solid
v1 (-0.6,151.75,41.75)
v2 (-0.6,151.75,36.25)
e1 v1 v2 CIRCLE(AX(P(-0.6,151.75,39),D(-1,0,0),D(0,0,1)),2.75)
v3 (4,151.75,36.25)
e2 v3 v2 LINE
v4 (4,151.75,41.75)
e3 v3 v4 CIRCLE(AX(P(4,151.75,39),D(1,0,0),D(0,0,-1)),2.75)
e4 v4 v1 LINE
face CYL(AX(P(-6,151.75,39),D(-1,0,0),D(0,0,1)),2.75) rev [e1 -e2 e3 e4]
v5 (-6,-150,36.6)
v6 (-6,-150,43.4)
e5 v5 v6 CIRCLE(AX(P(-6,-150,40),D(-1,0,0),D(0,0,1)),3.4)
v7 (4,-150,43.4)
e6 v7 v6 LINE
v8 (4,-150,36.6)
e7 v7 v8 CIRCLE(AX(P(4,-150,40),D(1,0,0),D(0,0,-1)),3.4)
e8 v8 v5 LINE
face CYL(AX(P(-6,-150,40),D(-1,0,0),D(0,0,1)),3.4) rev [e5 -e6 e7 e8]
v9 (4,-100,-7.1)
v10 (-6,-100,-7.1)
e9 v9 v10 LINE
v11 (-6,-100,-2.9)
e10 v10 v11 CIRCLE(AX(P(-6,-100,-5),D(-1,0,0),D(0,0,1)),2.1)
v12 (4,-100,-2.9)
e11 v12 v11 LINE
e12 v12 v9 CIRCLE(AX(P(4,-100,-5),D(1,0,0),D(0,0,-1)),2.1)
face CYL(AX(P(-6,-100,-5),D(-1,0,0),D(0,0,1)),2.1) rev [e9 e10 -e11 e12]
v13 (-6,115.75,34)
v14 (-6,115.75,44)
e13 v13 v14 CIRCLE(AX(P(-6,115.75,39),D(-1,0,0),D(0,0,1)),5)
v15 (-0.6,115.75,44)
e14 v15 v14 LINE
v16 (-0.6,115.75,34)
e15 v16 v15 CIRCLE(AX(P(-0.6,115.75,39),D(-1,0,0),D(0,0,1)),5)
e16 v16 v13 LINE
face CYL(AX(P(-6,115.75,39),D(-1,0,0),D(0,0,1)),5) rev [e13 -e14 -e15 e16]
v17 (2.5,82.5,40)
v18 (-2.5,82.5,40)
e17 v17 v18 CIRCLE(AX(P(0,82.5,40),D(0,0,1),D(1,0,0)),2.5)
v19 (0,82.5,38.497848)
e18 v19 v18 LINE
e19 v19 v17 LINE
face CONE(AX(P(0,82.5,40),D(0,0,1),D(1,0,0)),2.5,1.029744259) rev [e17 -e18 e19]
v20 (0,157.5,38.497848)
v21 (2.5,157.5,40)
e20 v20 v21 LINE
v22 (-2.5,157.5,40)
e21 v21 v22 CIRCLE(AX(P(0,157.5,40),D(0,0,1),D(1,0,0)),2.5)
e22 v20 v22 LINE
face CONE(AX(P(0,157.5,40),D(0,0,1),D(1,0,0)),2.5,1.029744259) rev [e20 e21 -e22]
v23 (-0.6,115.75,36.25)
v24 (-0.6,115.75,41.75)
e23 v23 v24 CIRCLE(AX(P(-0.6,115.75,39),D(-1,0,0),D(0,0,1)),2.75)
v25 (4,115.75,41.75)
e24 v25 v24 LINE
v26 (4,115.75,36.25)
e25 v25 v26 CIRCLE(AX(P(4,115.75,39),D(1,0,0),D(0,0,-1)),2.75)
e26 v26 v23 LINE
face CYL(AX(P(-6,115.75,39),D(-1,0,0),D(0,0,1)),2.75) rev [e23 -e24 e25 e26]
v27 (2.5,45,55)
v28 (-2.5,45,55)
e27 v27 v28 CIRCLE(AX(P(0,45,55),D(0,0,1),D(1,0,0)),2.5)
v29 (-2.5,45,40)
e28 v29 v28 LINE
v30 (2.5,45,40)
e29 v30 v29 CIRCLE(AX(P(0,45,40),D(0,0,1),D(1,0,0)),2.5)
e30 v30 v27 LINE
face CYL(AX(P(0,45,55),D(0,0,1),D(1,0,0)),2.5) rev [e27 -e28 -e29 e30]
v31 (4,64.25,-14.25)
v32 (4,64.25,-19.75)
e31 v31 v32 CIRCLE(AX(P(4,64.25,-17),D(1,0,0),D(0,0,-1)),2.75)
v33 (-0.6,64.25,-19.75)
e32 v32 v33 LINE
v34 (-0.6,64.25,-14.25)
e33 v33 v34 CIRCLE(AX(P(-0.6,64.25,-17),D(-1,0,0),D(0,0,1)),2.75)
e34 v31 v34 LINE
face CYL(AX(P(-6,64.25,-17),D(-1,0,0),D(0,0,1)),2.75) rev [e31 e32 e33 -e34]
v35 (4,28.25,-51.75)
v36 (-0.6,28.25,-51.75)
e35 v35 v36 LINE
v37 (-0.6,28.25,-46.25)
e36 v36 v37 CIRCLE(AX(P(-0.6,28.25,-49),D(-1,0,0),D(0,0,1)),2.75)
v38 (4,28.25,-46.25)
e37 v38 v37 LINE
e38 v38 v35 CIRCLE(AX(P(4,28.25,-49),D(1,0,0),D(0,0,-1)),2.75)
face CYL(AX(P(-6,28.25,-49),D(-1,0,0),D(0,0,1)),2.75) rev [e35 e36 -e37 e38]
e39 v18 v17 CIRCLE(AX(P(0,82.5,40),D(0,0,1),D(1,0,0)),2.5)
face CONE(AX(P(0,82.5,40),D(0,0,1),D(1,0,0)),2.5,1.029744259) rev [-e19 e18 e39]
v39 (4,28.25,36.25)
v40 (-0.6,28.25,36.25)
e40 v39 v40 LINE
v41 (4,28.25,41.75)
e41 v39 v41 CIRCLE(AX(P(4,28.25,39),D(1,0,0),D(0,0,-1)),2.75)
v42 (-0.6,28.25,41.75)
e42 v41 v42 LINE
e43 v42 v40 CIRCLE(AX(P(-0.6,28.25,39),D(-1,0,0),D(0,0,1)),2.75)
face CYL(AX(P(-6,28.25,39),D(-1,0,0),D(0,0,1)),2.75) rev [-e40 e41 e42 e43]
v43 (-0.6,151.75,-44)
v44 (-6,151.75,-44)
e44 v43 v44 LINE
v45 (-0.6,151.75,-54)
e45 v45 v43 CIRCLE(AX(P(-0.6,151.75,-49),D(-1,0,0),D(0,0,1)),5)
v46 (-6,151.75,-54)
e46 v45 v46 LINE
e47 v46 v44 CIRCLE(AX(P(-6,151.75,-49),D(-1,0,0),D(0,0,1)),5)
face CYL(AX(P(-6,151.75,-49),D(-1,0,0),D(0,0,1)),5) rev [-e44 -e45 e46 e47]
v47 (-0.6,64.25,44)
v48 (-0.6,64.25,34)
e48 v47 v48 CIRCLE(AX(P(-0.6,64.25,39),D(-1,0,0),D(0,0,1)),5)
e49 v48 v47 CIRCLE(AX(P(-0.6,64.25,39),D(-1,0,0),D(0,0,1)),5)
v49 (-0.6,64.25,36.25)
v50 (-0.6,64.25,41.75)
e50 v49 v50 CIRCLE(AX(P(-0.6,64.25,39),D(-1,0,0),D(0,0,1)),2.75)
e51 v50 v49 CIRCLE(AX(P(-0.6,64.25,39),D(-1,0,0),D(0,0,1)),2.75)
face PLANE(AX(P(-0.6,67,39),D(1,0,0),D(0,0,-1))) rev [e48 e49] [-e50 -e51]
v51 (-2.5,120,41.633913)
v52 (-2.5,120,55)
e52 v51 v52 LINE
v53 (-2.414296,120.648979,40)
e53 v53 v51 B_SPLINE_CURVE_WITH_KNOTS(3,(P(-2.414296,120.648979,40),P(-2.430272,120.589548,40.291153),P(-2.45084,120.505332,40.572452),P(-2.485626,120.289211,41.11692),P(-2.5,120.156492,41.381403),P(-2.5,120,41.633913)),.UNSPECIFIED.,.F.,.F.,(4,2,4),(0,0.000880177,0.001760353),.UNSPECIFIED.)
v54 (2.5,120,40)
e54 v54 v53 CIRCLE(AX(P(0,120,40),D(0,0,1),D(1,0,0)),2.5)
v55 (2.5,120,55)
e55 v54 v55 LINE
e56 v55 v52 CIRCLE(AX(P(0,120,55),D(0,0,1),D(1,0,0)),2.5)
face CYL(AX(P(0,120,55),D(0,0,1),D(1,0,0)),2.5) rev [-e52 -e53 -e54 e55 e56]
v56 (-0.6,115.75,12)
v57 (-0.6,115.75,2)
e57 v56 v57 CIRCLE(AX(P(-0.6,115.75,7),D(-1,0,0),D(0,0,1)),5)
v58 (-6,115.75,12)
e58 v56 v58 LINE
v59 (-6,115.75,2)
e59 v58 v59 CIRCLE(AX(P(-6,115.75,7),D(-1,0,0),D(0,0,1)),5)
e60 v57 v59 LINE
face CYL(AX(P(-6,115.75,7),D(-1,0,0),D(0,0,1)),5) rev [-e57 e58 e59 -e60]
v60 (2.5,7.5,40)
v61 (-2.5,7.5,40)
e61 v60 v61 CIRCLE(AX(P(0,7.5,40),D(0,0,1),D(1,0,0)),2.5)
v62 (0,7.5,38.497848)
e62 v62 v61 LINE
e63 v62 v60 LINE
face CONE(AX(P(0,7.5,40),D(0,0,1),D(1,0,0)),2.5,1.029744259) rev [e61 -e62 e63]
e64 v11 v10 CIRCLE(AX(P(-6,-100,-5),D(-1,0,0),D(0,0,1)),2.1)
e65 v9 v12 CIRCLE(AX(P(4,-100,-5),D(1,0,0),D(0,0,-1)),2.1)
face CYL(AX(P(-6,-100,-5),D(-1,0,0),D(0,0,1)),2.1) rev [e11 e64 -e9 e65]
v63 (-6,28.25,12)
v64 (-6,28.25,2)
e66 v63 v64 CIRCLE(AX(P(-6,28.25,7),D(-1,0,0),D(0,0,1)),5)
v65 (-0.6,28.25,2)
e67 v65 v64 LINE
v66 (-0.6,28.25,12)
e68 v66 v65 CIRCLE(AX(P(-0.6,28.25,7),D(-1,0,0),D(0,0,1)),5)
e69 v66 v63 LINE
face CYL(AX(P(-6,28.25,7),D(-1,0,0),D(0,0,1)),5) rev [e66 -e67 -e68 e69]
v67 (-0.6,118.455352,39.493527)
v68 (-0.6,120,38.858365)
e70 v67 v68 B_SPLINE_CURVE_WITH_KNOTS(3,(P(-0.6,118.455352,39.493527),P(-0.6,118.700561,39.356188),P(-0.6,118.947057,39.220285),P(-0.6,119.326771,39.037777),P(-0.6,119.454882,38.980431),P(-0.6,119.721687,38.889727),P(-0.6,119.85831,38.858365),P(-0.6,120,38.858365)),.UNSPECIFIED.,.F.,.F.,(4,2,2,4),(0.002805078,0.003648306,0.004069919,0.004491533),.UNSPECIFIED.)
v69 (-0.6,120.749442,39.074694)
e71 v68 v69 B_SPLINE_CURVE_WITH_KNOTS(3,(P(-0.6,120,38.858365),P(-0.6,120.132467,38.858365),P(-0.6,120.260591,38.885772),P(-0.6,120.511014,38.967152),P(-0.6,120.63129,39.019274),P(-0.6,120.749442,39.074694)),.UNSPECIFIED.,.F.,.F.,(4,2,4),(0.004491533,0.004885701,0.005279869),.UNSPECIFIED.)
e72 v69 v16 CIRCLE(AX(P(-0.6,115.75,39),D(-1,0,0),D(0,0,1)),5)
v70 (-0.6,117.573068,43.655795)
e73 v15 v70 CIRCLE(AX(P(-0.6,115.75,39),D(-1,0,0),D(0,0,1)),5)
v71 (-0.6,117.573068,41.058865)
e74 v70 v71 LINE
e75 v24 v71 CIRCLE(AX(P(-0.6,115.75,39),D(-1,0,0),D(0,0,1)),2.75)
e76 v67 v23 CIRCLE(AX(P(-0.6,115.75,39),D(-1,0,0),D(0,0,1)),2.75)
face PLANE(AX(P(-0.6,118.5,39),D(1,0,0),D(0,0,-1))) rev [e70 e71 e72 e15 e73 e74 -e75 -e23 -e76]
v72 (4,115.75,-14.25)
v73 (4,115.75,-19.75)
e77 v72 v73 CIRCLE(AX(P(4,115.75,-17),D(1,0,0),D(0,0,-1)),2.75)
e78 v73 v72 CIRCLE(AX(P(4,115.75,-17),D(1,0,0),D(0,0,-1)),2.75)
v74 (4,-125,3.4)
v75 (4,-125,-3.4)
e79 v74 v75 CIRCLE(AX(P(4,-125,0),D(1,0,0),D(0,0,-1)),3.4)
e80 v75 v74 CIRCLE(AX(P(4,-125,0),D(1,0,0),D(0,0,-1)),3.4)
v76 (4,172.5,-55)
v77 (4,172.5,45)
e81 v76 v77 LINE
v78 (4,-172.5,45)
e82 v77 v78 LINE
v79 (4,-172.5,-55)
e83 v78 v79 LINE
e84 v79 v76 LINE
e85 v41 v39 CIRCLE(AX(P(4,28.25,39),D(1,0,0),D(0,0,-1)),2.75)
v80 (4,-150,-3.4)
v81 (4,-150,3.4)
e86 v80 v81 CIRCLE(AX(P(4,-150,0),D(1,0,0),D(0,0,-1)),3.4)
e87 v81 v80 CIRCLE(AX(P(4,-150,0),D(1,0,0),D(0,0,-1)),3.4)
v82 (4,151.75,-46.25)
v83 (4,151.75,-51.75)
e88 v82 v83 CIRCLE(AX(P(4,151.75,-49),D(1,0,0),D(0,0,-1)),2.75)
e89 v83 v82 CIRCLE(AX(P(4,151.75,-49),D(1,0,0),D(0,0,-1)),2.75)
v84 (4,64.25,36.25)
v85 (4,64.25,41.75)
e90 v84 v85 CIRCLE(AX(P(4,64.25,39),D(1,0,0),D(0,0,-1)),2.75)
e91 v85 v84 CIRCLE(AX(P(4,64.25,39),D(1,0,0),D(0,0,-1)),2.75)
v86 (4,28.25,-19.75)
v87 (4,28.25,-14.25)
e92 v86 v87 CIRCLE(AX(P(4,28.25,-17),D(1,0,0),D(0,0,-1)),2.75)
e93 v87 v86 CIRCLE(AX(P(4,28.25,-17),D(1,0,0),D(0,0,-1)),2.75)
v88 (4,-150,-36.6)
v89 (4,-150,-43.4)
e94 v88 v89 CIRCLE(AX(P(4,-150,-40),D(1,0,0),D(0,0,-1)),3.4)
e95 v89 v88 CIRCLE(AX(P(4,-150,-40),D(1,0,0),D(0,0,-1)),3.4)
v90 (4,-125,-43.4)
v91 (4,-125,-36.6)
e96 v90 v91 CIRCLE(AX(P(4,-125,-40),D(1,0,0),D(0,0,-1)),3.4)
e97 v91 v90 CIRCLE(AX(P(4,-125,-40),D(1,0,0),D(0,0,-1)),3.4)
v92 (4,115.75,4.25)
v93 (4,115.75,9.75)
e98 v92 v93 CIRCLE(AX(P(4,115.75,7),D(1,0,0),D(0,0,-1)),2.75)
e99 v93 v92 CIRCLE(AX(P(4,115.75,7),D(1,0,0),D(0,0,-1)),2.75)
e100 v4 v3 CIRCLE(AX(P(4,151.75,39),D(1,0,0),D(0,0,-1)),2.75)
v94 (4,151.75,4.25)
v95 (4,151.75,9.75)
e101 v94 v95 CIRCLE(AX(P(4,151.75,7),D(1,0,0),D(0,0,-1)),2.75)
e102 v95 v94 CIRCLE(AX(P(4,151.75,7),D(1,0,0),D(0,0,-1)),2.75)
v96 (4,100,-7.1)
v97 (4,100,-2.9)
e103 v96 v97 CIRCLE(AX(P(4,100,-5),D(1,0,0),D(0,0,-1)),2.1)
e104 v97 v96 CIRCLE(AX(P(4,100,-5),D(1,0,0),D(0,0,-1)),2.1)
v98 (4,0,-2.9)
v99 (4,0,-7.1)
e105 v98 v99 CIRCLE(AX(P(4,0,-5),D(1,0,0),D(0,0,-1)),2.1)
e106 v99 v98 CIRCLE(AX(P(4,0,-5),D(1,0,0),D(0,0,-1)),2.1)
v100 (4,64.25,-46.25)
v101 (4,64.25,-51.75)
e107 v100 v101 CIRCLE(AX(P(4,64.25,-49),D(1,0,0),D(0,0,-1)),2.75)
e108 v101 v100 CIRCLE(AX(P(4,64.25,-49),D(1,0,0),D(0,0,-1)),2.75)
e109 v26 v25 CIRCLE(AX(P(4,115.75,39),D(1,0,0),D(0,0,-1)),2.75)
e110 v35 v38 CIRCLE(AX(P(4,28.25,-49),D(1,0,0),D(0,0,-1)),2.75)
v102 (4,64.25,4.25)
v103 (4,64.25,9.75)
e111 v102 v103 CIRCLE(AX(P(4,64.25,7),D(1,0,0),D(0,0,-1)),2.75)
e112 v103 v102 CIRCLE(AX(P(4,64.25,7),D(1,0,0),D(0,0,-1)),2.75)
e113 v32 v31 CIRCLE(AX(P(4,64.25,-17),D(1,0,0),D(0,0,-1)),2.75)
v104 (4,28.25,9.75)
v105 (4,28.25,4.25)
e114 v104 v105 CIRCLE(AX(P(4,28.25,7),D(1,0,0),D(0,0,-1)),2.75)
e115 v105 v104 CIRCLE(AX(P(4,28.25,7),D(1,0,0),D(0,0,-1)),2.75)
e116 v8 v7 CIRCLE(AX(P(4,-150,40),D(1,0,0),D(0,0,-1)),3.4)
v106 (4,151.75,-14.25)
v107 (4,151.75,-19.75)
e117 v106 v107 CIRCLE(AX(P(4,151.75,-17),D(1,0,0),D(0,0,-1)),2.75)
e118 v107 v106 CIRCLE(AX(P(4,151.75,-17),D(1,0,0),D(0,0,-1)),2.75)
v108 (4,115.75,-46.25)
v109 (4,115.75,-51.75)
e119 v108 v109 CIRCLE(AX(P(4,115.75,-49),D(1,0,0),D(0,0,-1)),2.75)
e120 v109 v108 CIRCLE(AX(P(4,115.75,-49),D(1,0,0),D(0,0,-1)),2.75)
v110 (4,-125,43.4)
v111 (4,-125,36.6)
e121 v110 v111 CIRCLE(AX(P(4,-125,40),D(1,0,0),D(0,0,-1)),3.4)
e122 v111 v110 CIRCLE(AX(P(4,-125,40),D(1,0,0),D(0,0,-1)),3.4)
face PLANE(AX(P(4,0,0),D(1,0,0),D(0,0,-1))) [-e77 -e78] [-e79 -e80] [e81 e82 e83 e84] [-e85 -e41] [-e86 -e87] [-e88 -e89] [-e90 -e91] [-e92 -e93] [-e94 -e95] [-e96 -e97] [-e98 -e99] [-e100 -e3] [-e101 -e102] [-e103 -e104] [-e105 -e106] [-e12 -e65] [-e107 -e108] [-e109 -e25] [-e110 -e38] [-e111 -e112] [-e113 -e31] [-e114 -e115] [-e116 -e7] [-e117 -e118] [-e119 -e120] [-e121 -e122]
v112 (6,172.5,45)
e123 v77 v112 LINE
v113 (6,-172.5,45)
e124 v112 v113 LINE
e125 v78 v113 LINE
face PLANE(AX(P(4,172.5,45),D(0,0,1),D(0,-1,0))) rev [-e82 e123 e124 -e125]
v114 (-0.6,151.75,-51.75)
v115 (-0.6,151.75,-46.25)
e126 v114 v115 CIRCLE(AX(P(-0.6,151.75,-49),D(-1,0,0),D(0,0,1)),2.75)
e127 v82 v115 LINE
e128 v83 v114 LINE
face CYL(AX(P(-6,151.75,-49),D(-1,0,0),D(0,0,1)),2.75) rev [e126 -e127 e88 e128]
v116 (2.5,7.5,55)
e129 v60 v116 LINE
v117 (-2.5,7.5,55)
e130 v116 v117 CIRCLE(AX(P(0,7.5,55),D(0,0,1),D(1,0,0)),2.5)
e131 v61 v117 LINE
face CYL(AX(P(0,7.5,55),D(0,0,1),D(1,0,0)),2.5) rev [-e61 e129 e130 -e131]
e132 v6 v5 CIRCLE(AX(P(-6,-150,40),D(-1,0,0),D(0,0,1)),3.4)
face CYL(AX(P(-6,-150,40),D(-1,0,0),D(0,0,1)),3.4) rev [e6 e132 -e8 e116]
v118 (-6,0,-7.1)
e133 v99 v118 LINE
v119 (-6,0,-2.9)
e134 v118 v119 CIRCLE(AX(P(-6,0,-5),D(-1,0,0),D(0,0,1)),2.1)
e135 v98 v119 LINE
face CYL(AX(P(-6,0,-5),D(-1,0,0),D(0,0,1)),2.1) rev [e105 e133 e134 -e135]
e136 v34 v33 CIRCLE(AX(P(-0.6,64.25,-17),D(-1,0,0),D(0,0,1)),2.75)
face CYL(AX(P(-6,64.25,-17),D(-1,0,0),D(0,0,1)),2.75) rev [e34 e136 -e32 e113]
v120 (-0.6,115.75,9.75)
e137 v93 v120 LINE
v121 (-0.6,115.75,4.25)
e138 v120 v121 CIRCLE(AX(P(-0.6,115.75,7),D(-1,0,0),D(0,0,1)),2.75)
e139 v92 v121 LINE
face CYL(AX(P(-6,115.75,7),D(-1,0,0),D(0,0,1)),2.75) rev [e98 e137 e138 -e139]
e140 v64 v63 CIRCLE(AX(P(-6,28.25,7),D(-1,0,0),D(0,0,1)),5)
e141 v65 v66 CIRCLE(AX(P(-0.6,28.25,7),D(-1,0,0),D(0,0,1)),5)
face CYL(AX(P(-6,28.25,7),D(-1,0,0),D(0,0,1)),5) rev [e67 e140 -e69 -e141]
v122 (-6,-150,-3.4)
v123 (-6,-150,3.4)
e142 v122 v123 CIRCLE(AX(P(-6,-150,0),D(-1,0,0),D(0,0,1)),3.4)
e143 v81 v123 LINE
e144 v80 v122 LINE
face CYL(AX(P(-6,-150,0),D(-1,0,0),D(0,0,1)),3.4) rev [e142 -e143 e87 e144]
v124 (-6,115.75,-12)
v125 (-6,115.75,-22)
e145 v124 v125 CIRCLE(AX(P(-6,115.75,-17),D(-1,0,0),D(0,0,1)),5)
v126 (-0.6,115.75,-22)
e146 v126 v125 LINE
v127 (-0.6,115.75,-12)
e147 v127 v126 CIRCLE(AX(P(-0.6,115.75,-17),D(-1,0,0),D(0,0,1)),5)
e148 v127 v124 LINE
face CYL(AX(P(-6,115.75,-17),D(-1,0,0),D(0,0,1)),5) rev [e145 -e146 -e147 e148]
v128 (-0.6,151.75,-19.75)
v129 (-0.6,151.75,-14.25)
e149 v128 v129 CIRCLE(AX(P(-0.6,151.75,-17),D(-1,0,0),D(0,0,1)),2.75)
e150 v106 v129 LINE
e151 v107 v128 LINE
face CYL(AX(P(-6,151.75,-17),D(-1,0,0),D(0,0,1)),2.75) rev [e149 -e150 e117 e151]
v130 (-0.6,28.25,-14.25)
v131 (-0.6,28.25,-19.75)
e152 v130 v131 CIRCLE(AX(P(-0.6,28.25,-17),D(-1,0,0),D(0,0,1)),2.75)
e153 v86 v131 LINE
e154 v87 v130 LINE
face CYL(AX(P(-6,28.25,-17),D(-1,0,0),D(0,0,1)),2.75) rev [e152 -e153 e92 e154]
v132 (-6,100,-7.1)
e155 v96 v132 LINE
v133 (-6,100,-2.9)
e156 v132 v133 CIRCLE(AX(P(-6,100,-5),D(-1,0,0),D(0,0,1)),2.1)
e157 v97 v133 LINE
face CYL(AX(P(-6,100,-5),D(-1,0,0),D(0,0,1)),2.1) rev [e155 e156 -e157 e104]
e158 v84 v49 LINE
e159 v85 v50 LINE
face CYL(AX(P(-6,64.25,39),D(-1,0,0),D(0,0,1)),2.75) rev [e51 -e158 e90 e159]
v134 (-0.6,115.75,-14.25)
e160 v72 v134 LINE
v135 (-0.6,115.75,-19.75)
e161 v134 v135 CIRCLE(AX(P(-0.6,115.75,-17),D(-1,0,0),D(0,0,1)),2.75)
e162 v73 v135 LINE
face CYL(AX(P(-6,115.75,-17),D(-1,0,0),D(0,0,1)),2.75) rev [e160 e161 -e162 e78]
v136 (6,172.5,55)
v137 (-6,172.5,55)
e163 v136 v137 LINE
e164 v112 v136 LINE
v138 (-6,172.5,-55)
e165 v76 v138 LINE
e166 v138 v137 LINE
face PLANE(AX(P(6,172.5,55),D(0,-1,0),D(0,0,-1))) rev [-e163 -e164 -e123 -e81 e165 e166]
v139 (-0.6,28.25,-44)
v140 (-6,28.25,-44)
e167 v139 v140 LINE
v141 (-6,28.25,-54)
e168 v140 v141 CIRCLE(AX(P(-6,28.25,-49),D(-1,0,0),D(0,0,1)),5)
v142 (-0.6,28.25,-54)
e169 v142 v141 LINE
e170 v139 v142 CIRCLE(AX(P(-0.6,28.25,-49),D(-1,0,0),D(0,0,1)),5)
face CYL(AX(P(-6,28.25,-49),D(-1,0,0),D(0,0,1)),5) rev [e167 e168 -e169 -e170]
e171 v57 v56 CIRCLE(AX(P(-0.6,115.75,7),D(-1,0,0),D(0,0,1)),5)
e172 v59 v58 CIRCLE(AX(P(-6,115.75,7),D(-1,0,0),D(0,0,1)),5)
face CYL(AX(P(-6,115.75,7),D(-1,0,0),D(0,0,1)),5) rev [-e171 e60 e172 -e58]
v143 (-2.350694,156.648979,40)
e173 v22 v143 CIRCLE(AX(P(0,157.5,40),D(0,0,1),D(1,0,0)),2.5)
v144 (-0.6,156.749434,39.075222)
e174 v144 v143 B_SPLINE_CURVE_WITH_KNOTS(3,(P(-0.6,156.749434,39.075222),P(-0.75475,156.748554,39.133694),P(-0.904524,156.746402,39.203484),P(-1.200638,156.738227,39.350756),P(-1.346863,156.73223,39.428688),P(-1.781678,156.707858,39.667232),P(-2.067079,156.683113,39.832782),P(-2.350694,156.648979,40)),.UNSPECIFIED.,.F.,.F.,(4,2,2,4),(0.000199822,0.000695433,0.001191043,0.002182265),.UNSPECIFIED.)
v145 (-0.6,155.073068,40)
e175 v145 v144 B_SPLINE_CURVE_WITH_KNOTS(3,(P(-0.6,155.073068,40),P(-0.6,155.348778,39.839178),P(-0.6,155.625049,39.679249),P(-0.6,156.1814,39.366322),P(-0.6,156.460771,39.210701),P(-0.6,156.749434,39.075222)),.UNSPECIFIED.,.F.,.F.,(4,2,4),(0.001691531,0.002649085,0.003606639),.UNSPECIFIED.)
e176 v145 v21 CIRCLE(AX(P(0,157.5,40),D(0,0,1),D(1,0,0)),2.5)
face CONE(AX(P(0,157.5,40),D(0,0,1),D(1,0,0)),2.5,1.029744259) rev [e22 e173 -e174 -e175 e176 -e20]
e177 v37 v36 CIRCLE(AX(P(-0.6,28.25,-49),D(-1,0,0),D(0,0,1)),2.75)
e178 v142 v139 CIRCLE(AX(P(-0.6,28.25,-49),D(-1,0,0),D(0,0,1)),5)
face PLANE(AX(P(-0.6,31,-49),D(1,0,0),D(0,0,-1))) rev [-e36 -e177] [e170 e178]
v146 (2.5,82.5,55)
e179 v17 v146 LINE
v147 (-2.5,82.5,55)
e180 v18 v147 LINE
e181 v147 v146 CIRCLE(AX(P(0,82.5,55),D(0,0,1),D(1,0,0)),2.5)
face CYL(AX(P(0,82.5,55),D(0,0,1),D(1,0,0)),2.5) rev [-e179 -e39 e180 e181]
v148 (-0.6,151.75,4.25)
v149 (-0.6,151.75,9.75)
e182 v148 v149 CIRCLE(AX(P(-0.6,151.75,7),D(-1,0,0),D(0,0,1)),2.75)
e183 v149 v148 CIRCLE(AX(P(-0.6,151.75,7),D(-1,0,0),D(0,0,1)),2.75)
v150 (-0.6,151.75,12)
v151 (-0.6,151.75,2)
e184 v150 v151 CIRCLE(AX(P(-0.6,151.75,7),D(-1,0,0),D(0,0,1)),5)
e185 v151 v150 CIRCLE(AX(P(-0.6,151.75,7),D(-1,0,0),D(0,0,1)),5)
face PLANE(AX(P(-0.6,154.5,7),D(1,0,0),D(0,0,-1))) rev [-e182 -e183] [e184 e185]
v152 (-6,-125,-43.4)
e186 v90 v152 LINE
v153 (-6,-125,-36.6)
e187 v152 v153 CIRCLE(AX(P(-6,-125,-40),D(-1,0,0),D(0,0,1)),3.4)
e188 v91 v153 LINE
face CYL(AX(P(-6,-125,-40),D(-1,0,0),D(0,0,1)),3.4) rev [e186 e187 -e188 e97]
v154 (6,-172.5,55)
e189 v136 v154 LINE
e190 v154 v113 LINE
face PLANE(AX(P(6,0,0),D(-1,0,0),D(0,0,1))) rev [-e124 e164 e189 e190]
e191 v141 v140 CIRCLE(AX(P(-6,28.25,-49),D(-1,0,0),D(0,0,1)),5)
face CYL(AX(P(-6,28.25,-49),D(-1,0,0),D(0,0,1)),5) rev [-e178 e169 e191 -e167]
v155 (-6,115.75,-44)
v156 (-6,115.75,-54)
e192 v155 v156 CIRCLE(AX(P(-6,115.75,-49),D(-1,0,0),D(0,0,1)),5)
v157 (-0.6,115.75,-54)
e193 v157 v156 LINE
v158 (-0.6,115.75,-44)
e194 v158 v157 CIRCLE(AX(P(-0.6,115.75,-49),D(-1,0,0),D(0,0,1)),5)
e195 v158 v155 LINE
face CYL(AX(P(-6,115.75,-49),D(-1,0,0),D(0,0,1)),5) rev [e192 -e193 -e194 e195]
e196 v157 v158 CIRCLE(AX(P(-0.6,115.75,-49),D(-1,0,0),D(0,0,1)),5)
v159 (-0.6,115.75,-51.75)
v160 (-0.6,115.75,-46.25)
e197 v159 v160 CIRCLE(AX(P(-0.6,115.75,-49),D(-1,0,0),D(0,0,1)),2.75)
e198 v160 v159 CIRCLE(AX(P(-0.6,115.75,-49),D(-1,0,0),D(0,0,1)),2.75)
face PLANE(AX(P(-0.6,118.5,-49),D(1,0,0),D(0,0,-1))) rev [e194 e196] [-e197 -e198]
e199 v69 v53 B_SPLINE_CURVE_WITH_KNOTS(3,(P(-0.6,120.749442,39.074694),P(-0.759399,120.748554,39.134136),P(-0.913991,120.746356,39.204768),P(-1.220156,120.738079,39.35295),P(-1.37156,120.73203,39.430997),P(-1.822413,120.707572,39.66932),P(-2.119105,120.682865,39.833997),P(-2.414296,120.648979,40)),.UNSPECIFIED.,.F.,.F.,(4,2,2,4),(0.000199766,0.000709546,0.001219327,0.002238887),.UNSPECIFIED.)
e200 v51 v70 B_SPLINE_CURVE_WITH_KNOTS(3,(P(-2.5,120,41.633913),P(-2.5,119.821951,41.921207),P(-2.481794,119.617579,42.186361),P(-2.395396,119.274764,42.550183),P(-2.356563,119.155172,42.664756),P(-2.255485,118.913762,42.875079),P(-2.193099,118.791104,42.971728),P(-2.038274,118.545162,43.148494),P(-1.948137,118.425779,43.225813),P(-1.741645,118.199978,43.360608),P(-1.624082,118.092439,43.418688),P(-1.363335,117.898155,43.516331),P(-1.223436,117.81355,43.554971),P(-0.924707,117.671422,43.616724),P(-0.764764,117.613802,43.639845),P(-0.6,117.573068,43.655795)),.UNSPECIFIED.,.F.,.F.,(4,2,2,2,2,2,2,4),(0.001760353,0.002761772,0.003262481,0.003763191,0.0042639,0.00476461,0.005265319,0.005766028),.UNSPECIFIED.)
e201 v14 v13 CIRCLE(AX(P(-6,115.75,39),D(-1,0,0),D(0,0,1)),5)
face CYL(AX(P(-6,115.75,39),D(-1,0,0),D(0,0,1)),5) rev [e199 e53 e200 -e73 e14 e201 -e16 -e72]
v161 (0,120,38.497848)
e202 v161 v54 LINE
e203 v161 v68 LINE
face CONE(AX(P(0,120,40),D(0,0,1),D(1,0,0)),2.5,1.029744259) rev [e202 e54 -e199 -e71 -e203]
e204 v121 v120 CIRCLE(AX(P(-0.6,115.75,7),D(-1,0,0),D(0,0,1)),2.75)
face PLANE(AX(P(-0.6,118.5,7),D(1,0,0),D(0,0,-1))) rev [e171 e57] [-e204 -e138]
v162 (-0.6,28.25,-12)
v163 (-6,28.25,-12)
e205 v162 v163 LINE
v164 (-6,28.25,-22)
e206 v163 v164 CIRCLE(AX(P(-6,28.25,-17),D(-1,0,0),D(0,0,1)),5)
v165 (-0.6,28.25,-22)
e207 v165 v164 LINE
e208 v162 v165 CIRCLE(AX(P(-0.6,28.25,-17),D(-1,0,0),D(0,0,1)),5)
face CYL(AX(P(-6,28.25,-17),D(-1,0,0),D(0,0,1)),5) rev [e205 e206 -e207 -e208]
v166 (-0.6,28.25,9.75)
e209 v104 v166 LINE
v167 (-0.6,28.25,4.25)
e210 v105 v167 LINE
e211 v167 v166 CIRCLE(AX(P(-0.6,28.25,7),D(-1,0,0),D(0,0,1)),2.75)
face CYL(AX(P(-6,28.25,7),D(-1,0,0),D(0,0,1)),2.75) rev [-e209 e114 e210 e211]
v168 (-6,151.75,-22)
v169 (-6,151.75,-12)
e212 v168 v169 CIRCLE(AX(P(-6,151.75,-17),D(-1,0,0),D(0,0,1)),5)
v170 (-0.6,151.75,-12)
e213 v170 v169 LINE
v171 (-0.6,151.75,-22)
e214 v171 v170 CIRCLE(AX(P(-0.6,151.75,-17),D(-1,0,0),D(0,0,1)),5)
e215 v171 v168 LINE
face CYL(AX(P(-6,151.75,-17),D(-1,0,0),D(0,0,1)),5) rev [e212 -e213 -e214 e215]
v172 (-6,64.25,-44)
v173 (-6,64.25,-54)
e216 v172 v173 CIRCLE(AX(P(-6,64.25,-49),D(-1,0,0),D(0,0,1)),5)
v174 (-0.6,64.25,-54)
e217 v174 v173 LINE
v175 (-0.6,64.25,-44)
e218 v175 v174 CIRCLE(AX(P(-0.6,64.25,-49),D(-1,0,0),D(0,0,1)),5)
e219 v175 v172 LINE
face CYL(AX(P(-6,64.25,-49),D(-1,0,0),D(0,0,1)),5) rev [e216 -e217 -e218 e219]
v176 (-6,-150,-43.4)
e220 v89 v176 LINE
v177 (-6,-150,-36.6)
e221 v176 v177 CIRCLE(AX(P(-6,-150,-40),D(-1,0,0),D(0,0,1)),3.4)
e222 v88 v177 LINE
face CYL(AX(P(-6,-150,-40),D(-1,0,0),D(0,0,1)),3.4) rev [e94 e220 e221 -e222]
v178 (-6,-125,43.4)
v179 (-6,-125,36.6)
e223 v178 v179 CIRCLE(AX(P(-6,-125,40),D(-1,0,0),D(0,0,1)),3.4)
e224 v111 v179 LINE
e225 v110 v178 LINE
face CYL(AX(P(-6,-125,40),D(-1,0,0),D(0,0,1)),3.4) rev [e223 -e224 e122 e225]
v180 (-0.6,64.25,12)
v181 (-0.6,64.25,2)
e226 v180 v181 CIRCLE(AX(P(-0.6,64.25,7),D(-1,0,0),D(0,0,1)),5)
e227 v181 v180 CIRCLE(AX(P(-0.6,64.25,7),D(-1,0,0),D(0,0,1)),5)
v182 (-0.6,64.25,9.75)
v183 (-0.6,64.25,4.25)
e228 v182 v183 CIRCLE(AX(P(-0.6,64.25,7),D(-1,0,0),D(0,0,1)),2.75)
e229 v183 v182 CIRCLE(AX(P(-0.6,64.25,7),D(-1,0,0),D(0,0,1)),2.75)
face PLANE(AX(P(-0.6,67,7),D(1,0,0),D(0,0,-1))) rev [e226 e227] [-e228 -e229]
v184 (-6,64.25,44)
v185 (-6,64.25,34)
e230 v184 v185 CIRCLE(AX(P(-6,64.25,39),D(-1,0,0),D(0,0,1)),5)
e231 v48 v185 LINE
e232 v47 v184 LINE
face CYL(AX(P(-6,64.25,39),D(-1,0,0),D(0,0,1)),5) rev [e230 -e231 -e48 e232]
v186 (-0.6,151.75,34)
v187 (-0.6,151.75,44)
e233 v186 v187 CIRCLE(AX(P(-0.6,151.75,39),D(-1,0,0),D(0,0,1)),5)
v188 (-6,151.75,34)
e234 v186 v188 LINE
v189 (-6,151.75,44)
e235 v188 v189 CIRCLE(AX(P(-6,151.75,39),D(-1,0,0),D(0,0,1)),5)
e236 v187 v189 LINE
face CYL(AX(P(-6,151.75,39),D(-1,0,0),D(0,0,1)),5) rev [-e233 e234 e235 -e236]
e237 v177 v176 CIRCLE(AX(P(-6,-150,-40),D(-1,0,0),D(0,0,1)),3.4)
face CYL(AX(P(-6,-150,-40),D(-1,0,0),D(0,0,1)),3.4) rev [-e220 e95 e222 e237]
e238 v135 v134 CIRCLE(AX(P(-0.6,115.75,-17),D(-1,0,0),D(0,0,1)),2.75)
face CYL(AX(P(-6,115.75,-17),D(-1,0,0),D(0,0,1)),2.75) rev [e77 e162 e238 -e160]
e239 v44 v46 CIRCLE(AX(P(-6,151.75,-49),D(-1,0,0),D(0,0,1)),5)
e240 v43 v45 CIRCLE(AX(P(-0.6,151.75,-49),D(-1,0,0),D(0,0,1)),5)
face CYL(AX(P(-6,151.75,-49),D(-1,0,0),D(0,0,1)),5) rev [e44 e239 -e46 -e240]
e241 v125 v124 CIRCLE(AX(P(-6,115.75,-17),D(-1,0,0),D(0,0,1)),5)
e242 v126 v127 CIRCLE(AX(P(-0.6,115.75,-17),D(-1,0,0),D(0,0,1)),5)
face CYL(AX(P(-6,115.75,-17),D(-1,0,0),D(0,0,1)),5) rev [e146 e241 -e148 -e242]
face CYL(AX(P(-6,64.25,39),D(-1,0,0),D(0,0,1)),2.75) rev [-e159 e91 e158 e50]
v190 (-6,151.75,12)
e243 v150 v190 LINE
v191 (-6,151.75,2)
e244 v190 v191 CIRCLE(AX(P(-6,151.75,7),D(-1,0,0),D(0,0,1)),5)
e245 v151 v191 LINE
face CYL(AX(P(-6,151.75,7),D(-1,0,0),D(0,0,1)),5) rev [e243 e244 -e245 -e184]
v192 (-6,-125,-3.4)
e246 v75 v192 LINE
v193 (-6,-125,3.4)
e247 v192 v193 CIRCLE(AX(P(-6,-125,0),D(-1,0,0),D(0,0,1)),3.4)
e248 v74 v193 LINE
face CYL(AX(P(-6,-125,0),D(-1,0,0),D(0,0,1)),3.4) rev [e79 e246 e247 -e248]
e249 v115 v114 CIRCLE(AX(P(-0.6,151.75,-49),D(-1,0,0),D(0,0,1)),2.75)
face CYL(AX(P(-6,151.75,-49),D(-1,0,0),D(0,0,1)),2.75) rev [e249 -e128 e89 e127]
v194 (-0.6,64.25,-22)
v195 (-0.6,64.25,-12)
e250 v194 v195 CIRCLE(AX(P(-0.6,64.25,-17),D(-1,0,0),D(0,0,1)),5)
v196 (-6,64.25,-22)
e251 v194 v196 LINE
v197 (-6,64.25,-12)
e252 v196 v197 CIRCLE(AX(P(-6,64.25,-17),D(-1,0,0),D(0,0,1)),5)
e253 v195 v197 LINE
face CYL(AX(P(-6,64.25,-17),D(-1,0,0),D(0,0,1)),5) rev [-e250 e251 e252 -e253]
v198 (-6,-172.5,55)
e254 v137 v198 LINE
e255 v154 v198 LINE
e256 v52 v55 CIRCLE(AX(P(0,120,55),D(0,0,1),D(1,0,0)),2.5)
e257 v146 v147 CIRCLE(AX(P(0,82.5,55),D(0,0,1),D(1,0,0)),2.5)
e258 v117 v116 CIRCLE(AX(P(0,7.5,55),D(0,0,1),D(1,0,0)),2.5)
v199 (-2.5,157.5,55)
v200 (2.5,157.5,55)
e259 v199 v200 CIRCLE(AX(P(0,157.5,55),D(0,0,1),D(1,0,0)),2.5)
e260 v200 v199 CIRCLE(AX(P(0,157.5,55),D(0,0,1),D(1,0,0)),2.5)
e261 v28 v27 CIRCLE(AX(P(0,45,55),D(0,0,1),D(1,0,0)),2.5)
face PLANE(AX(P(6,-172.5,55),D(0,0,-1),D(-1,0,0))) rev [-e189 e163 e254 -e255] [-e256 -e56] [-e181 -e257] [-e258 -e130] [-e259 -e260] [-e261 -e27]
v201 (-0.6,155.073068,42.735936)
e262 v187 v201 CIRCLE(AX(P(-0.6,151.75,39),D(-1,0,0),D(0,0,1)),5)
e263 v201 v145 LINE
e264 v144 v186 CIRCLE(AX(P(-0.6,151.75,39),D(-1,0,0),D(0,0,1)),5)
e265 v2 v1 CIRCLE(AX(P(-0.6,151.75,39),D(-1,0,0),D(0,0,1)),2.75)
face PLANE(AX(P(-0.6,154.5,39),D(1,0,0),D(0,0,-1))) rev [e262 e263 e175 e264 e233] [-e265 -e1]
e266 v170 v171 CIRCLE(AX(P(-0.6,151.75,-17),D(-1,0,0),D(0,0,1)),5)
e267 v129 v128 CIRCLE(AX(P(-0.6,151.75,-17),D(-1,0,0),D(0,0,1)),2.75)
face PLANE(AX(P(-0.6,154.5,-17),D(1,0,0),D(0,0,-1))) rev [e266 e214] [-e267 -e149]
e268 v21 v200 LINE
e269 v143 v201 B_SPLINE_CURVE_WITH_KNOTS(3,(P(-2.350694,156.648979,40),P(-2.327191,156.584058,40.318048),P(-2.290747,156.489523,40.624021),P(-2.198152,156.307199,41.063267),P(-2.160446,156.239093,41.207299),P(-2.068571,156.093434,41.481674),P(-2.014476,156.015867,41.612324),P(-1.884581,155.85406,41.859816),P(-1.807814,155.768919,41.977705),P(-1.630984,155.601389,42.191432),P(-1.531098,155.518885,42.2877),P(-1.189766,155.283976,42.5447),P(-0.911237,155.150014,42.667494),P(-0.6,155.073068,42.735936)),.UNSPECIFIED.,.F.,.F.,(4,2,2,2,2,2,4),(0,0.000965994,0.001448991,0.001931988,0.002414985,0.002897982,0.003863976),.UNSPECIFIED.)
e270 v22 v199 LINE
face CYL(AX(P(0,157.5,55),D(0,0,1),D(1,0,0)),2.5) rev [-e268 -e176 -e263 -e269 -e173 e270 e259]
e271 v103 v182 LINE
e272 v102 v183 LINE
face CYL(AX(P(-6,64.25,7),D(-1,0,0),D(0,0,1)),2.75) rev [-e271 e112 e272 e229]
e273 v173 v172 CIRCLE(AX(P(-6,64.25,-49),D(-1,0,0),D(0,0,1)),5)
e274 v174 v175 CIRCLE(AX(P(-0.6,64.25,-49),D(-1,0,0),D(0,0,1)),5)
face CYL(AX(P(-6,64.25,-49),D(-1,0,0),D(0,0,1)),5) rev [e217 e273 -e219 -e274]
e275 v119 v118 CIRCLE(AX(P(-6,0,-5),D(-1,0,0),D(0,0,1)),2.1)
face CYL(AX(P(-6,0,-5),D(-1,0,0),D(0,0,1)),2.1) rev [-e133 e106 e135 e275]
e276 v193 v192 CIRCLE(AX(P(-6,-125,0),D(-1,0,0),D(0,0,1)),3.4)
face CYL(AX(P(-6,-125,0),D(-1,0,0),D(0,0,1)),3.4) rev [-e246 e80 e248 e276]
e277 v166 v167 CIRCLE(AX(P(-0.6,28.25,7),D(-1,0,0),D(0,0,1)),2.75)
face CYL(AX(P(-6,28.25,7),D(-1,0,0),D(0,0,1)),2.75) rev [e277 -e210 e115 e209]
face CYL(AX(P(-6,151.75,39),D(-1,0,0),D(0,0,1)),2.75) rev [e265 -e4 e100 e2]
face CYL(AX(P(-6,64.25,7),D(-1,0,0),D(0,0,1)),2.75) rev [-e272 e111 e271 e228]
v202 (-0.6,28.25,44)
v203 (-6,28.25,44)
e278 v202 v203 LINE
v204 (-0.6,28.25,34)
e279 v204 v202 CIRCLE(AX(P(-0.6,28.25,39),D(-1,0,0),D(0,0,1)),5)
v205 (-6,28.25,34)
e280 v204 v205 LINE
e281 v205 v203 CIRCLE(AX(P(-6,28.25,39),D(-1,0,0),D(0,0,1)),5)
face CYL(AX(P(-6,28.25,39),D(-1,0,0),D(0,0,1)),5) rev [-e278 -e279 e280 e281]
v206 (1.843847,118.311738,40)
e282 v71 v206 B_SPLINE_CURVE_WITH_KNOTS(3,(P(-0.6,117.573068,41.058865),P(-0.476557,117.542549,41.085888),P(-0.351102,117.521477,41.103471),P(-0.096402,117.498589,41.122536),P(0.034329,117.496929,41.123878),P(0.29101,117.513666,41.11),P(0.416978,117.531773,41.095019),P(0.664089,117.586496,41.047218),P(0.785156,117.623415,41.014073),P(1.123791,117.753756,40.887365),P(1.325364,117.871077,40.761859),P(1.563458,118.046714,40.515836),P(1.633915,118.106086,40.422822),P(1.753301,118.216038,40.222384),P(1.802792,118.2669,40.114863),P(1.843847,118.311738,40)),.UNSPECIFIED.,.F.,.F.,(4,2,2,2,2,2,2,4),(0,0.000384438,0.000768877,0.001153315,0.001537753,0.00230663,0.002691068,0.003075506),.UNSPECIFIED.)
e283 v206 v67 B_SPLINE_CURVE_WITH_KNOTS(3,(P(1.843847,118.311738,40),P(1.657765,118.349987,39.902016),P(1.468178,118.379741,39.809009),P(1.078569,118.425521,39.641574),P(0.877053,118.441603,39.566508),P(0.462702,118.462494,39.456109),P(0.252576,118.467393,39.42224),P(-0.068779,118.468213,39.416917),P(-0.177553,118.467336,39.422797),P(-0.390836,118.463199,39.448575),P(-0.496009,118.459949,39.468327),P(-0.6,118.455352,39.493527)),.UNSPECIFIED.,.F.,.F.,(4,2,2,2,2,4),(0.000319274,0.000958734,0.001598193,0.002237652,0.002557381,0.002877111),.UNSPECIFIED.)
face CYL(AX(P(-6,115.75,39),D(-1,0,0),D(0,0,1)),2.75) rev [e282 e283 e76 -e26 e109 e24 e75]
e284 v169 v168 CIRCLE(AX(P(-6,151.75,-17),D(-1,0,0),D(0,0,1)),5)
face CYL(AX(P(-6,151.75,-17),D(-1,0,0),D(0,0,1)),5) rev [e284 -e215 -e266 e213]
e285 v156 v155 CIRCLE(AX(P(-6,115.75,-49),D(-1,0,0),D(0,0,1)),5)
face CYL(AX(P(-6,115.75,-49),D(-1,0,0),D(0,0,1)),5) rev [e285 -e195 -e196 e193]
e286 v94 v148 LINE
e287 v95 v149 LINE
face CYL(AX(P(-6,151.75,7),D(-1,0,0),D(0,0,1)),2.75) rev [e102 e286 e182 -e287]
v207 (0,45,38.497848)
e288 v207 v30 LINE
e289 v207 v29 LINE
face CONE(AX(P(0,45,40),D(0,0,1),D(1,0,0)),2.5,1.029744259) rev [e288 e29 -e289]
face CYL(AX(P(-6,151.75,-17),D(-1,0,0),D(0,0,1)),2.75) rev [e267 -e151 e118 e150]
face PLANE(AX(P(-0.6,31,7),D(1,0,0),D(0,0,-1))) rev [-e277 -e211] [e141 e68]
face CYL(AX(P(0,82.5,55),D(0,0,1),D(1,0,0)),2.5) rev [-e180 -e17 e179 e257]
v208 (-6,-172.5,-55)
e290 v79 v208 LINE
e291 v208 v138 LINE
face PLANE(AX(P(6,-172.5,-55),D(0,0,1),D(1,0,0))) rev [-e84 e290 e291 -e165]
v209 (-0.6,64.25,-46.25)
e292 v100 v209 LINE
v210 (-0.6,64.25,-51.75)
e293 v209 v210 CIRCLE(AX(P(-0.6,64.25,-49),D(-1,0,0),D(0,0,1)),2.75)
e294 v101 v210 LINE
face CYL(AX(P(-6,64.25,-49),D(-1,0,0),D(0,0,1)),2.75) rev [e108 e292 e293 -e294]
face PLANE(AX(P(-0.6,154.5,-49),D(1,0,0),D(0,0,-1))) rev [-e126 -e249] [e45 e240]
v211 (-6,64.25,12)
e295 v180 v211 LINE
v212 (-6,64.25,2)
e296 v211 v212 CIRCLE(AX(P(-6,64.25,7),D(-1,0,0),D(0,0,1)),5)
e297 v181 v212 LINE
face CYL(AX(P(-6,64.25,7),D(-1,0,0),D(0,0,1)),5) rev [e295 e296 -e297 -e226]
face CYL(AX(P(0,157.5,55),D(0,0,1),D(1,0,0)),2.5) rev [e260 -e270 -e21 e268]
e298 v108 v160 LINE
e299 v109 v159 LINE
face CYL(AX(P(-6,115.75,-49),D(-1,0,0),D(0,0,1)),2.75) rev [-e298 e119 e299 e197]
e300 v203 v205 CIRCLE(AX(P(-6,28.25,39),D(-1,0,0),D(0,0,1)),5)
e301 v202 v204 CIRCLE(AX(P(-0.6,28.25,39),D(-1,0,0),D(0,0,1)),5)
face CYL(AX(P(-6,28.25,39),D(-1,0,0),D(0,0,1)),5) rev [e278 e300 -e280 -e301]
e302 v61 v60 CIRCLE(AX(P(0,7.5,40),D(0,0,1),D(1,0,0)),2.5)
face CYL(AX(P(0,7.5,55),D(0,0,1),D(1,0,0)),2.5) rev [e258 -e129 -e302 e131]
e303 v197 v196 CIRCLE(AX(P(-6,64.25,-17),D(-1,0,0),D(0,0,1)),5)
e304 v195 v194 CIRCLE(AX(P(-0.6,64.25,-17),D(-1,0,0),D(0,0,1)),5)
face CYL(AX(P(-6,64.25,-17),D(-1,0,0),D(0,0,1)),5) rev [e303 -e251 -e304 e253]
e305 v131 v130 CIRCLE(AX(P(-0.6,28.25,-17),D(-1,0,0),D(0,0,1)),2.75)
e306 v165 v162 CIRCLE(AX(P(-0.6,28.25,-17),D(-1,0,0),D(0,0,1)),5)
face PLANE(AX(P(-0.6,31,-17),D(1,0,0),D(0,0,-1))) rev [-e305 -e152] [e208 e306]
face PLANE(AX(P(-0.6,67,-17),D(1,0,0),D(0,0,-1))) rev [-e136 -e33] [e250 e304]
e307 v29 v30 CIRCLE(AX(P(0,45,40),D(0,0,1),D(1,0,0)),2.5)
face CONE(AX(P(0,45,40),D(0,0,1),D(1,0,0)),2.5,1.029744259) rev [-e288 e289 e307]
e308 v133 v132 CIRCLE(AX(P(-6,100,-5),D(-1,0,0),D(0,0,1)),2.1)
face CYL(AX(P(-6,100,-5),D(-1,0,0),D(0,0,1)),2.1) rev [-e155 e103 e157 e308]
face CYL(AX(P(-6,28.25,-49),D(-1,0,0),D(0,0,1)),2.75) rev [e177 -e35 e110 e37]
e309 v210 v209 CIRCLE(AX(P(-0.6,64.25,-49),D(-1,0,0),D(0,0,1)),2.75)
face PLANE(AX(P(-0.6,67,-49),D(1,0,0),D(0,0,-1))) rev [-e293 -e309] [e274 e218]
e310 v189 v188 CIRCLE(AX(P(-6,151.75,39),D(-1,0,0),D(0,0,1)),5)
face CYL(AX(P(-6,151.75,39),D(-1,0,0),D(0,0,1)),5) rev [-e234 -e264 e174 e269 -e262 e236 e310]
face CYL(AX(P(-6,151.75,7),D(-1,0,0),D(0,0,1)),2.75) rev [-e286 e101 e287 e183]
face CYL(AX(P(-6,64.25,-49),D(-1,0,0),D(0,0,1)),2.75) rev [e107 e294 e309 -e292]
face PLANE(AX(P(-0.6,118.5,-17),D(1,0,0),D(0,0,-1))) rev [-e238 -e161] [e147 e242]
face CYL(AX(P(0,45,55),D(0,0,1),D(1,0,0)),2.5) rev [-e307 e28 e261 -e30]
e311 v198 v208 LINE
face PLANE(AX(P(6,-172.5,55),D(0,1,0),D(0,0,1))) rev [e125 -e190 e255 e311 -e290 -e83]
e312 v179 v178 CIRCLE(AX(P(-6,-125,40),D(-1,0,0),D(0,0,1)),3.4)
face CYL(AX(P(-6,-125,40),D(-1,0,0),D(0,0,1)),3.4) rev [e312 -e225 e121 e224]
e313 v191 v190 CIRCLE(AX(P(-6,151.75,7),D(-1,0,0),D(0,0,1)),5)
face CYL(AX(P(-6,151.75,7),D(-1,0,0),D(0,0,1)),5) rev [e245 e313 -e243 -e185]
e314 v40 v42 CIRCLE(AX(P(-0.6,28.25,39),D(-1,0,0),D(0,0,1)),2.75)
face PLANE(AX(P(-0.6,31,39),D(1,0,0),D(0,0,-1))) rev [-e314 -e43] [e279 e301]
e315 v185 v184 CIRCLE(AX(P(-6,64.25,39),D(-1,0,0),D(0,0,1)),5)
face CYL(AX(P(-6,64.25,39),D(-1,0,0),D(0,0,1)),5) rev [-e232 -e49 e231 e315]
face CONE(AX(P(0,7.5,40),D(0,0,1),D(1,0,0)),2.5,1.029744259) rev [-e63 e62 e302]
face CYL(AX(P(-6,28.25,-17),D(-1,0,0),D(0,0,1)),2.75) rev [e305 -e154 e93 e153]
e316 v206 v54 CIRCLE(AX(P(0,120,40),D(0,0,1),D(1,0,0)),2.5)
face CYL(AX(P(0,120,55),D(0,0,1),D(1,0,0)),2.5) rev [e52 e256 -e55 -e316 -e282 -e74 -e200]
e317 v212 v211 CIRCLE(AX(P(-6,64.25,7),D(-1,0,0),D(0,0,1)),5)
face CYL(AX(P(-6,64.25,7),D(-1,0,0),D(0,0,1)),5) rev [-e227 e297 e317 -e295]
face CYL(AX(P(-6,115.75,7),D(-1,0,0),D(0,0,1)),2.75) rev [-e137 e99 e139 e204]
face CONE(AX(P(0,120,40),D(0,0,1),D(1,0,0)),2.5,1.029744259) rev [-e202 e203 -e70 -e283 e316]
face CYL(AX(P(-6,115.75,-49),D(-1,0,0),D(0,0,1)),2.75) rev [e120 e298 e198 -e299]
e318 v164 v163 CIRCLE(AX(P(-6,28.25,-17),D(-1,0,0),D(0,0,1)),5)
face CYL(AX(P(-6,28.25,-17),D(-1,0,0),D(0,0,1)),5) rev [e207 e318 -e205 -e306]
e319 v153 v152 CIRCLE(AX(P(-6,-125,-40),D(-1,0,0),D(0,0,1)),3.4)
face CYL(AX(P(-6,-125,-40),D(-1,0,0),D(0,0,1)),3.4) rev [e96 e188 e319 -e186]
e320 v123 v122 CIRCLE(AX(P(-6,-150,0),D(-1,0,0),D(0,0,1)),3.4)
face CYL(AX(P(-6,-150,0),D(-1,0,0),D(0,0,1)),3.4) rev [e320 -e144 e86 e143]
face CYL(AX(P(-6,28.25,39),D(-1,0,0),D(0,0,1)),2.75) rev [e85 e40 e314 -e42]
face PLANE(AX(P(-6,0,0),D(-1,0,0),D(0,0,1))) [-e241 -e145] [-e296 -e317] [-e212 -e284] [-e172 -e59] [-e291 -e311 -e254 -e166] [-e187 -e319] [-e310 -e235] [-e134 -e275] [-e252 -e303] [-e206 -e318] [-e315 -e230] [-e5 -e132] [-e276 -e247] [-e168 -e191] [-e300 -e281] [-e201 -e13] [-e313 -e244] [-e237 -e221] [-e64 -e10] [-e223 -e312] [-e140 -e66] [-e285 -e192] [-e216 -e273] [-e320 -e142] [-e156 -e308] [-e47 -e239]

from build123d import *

# Parameters (mm, degrees)
SKETCH_1_W                   = 110
SKETCH_1_H                   = 345
EXTRUDE_1_DEPTH              = 6
SKETCH_2_W                   = 100
SKETCH_2_H                   = 345
CUT_EXTRUDE_1_DEPTH          = 2
HOLE_WIZARD_M5_1_D           = 5.5
HOLE_WIZARD_M5_1_CBORE_D     = 10
HOLE_WIZARD_M5_1_CBORE_DEPTH = 5.4
HOLE_WIZARD_M8_1_D           = 6.8
HOLE_WIZARD_M6_1_D           = 5
HOLE_WIZARD_M6_1_DEPTH       = 15
HOLE_WIZARD_M6_1_TIP         = 1.502151548
HOLE_WIZARD_M5_1_2_D         = 4.2


with BuildPart() as part:
    # 草图1 → 凸台-拉伸1 (new, symmetric)
    with BuildSketch(Plane(origin=(0, 0, 0), x_dir=(0, 0, -1), z_dir=(1, 0, 0))):
        Rectangle(SKETCH_1_W, SKETCH_1_H)
    extrude(amount=EXTRUDE_1_DEPTH, both=True)

    # 草图2 → 切除-拉伸1 (cut)
    with BuildSketch(Plane(origin=(6, 0, 0), x_dir=(0, 0, -1), z_dir=(1, 0, 0))):
        with Locations((5, 0)):
            Rectangle(SKETCH_2_W, SKETCH_2_H)
    extrude(amount=-CUT_EXTRUDE_1_DEPTH, mode=Mode.SUBTRACT)

    # Hole Wizard M5 _1 (through all)
    with Locations(Plane.ZY.offset(6)):
        with Locations((-49, 151.75), (-17, 151.75), (7, 151.75), (39, 151.75), (39, 115.75), (7, 115.75), (-17, 115.75), (-49, 115.75), (-49, 64.25), (-49, 28.25), (-17, 64.25), (-17, 28.25), (7, 64.25), (7, 28.25), (39, 64.25), (39, 28.25)):
            CounterBoreHole(HOLE_WIZARD_M5_1_D / 2, HOLE_WIZARD_M5_1_CBORE_D / 2, HOLE_WIZARD_M5_1_CBORE_DEPTH)

    # M8 螺纹孔1 (through all)
    with Locations(Plane.ZY.offset(6)):
        with Locations((-40, -125), (-40, -150), (0, -125), (0, -150), (40, -125), (40, -150)):
            Hole(HOLE_WIZARD_M8_1_D / 2)

    # M6 螺纹孔1
    with Locations(Plane.XY.offset(55)):
        with Locations((0, 7.5), (0, 45), (0, 82.5), (0, 120), (0, 157.5)):
            Hole(HOLE_WIZARD_M6_1_D / 2, depth=HOLE_WIZARD_M6_1_DEPTH)
            with Locations((0, 0, -(HOLE_WIZARD_M6_1_DEPTH + HOLE_WIZARD_M6_1_TIP / 2))):  # 118° drill point
                Cone(0, HOLE_WIZARD_M6_1_D / 2, HOLE_WIZARD_M6_1_TIP, mode=Mode.SUBTRACT)

    # Hole Wizard M5 _1 2 (through all)
    with Locations(Plane.ZY.offset(6)):
        with Locations((-5, 185), (-5, 100), (-5, 0), (-5, -100)):
            Hole(HOLE_WIZARD_M5_1_2_D / 2)


solid = part.part
